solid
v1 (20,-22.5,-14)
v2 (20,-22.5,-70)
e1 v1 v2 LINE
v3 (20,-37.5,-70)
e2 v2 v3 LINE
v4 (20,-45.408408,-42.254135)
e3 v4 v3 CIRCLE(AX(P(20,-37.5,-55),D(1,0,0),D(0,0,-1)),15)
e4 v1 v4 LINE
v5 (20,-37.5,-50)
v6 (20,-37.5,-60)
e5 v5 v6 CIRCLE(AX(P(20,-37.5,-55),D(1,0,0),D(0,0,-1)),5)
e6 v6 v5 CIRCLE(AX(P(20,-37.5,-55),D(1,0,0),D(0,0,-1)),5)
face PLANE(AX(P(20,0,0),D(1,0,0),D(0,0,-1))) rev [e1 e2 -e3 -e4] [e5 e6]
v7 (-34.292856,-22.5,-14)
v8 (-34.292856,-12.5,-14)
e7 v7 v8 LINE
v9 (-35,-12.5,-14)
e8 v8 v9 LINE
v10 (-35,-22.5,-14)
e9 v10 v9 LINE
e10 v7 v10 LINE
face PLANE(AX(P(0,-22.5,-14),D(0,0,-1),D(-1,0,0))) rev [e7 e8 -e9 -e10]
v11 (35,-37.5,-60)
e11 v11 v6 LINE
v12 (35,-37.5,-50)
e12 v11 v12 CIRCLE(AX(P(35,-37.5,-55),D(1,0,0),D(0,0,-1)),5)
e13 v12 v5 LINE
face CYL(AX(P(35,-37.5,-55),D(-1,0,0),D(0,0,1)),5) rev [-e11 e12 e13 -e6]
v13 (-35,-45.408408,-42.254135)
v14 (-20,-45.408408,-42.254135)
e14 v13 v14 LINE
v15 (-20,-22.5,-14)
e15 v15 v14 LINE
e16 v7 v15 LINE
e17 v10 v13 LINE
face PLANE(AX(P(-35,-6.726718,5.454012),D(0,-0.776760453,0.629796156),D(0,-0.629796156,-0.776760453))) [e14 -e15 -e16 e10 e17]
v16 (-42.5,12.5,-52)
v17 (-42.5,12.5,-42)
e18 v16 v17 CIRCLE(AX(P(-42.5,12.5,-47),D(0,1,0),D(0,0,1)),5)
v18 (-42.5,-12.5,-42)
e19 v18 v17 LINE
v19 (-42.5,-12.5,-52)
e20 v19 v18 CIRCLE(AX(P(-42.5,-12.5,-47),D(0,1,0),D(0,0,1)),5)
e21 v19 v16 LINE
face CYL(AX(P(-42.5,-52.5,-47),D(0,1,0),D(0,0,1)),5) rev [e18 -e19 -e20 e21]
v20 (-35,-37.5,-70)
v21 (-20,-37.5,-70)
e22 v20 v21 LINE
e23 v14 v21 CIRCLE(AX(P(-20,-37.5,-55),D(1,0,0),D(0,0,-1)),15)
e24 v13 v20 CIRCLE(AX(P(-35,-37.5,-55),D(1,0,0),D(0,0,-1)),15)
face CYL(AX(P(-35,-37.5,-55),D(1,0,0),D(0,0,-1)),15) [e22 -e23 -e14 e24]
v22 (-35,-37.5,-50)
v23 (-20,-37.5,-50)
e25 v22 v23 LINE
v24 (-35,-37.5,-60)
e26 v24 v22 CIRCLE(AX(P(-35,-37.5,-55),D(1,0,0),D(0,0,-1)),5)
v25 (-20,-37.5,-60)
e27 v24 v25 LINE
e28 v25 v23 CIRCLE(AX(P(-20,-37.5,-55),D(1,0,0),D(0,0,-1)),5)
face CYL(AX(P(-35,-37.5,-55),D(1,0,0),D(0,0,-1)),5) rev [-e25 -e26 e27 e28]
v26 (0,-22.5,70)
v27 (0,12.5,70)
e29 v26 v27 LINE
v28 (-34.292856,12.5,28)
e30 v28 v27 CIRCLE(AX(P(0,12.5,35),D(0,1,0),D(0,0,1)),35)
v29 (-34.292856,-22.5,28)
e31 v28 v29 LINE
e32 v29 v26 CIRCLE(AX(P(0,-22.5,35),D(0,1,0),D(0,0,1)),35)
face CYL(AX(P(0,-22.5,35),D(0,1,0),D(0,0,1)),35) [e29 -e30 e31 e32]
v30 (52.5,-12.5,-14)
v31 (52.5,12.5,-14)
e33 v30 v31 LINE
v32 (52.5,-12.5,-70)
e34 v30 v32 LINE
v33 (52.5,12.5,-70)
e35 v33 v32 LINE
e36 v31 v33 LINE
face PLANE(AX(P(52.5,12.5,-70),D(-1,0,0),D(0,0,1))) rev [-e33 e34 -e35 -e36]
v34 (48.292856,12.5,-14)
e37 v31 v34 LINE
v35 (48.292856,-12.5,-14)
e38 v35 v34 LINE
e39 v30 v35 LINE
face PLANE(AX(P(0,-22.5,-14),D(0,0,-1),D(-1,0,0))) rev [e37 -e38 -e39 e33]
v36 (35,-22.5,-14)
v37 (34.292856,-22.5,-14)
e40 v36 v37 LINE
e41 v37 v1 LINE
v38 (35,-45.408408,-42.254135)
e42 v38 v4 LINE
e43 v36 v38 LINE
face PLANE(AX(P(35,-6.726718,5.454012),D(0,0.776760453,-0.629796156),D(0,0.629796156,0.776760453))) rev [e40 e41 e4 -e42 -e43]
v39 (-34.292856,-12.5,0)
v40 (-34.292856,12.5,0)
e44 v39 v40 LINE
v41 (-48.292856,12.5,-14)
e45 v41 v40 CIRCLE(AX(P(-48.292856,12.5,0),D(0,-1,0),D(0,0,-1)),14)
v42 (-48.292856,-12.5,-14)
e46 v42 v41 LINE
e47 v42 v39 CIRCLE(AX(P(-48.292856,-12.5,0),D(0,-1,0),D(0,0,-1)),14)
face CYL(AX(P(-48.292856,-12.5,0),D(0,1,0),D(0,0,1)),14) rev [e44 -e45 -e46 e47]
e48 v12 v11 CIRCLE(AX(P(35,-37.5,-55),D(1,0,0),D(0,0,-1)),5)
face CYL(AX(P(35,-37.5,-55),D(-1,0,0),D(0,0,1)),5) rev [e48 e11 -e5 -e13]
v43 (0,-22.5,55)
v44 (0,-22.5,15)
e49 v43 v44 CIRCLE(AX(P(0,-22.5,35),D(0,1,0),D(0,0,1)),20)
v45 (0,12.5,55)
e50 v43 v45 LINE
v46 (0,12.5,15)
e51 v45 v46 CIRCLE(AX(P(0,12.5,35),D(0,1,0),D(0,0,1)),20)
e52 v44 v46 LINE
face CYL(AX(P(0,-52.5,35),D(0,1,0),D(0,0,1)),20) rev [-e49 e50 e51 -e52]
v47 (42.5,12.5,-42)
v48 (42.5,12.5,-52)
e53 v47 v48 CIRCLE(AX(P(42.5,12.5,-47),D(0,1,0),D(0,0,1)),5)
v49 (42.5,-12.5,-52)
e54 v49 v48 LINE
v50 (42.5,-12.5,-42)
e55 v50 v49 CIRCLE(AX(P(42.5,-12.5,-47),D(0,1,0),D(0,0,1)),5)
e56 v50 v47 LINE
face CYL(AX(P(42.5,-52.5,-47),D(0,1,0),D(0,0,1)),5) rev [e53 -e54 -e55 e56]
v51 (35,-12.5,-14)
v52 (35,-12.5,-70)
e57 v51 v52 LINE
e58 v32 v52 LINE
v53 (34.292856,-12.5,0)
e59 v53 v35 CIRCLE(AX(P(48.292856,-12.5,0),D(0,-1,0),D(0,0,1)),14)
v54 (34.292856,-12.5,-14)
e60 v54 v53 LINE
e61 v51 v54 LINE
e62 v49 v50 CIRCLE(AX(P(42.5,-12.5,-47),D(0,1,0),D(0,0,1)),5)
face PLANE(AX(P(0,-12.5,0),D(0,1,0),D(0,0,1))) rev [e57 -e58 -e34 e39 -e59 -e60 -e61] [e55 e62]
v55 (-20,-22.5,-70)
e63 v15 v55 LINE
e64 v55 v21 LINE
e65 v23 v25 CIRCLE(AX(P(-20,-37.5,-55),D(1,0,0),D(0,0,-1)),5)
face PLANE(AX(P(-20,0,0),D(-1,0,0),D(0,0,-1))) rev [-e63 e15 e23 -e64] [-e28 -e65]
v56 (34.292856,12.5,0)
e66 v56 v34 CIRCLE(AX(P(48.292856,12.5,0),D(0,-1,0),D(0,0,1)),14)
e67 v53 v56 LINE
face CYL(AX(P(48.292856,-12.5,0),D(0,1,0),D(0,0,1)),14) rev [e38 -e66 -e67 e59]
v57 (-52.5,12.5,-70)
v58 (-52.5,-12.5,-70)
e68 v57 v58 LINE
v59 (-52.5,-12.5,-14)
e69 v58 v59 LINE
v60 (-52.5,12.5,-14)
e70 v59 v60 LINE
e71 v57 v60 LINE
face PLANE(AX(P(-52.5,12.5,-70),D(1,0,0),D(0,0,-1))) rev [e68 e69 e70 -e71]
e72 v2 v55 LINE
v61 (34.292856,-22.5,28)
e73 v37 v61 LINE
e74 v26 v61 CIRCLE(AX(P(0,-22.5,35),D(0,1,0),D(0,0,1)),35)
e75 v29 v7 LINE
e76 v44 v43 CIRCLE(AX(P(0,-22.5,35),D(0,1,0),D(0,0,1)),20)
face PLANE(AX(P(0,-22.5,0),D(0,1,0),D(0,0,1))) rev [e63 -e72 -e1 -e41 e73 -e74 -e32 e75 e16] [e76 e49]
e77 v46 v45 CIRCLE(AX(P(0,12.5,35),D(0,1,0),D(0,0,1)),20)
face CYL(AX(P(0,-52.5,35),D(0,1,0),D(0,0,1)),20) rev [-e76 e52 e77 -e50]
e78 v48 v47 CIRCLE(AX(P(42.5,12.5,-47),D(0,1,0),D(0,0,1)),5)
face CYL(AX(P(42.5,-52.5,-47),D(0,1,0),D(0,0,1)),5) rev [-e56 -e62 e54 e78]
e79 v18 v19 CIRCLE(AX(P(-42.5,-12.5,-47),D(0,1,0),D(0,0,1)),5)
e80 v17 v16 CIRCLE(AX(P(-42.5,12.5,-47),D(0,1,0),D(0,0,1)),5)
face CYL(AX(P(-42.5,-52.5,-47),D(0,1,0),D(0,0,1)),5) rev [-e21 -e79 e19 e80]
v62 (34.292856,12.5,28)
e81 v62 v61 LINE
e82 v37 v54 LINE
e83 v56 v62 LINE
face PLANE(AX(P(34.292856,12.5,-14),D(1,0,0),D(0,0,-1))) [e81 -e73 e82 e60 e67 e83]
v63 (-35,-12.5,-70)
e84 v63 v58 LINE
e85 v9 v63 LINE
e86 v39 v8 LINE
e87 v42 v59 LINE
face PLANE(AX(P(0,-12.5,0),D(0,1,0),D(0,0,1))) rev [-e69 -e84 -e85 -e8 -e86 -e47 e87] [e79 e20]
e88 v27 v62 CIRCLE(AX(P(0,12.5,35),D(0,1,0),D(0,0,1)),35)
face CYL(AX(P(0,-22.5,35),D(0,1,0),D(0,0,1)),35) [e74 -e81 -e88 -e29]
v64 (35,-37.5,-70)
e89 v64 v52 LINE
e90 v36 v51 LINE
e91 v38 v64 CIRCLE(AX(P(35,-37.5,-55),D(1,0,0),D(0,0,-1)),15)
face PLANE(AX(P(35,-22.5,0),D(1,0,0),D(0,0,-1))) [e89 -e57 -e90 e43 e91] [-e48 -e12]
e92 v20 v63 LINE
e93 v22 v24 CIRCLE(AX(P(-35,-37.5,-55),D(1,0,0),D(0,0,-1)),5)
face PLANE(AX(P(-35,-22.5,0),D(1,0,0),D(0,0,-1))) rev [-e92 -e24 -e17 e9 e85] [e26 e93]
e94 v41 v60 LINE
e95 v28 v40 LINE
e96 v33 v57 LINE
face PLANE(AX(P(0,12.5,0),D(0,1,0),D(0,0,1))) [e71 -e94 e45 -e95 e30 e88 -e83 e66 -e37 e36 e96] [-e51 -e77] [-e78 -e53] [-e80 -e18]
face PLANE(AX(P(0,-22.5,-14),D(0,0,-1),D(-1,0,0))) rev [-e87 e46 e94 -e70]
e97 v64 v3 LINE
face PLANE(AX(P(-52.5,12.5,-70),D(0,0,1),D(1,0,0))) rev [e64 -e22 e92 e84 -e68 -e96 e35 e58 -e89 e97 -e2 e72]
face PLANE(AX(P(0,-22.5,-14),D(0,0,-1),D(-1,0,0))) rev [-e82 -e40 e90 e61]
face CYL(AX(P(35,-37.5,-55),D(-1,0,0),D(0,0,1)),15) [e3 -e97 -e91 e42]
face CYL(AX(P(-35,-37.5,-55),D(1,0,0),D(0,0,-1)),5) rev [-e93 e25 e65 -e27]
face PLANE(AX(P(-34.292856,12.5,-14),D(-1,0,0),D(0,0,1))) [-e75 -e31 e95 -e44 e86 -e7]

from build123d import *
from build123d.topology import SkipClean

# Parameters (mm, degrees)
BASE_PLATE_SKETCH_140X105_W  = 105
BASE_PLATE_SKETCH_140X105_H  = 140
BASE_PLATE_DEPTH             = 12.5
HUB_BOSS_DEPTH               = 35
BORE_RELIEF_56_DEPTH         = 95.240384125
FILLER_START                 = -35
FILLER_BOSS_DEPTH            = 35
LUG_BOSS_DEPTH               = 25
SIDE_START                   = 20
SIDE_EAR_SKETCH_R            = 5
SIDE_EAR_DEPTH               = 15
MOUNTING_HOLES_SKETCH_10_R   = 5
MOUNTING_HOLES_SKETCH_10_R_2 = 20
MOUNTING_HOLES_10_DEPTH      = 110.001146783


with BuildPart() as part:
    # Base Plate Sketch 140x105 → Base Plate (new, symmetric)
    with BuildSketch(Plane(origin=(0, 0, 0), x_dir=(1, 0, 0), z_dir=(0, 1, 0))):
        Rectangle(BASE_PLATE_SKETCH_140X105_W, BASE_PLATE_SKETCH_140X105_H)
    extrude(amount=BASE_PLATE_DEPTH, both=True)

    # Hub Boss Sketch → Hub Boss (add)
    with BuildSketch(Plane(origin=(0, 12.5, 0), x_dir=(1, 0, 0), z_dir=(0, 1, 0))):
        with BuildLine():
            Line((-17.5, 70), (-35, 70))
            Line((-35, 70), (-35, 14))
            Line((-35, 14), (-35, -35))
            ThreePointArc((-35, -35), (-24.748737337, -59.748737346), (1.3e-08, -70))
            ThreePointArc((1.3e-08, -70), (24.748737346, -59.748737337), (35, -35))
            Line((35, -35), (35, 14))
            Line((35, 14), (35, 70))
            Line((35, 70), (17.5, 70))
            Line((17.5, 70), (-17.5, 70))
        make_face()
    extrude(amount=-HUB_BOSS_DEPTH)

    # Bore Relief Sketch _56 → Bore Relief _56 (cut, through all)
    with SkipClean():  # the faces are left unmerged after this step: merging them gives an invalid solid
        with BuildSketch(Plane(origin=(0, 12.5, 0), x_dir=(1, 0, 0), z_dir=(0, 1, 0))):
            with BuildLine():
                Line((-52.5, -70), (6e-09, -70))
                ThreePointArc((6e-09, -70), (-24.748737339, -59.748737344), (-35, -35))
                ThreePointArc((-35, -35), (-32.267021942, -21.441264992), (-24.494897428, -10))
                ThreePointArc((-24.494897428, -10), (-21.331375002, 5.291502622), (-34.292856399, 14))
                Line((-34.292856399, 14), (-52.5, 14))
                Line((-52.5, 14), (-52.5, -70))
            make_face()
            with BuildLine():
                Line((52.5, -70), (52.5, 14))
                Line((52.5, 14), (34.292856399, 14))
                ThreePointArc((34.292856399, 14), (21.331375002, 5.291502622), (24.494897428, -10))
                ThreePointArc((24.494897428, -10), (32.267021942, -21.441264992), (35, -35))
                ThreePointArc((35, -35), (24.748737344, -59.748737339), (6e-09, -70))
                Line((6e-09, -70), (52.5, -70))
            make_face()
        extrude(amount=-BORE_RELIEF_56_DEPTH, mode=Mode.SUBTRACT)

    # Filler Boss Sketch → Filler Boss (add)
    with SkipClean():  # the faces are left unmerged after this step: merging them gives an invalid solid
        with BuildSketch(Plane.XZ.offset(22.5).offset(FILLER_START)):
            with BuildLine():
                Line((-34.292856399, -14), (-34.292856399, 28))
                ThreePointArc((-34.292856399, 28), (-30.740852298, 18.266799469), (-24.494897428, 10))
                ThreePointArc((-24.494897428, 10), (-21.331375002, -5.291502622), (-34.292856399, -14))
            make_face()
            with BuildLine():
                Line((34.292856399, -14), (34.292856399, 28))
                ThreePointArc((34.292856399, 28), (30.740852298, 18.266799469), (24.494897428, 10))
                ThreePointArc((24.494897428, 10), (21.331375002, -5.291502622), (34.292856399, -14))
            make_face()
        extrude(amount=FILLER_BOSS_DEPTH)

    # Lug Boss Sketch → Lug Boss (add)
    with SkipClean():  # the faces are left unmerged after this step: merging them gives an invalid solid
        with BuildSketch(Plane(origin=(0, 12.5, 0), x_dir=(1, 0, 0), z_dir=(0, 1, 0))):
            with BuildLine():
                Line((48.292856399, 14), (34.292856399, 14))
                Line((34.292856399, 14), (34.292856399, 0))
                ThreePointArc((34.292856399, 0), (38.393361462, 9.899494937), (48.292856399, 14))
            make_face()
            with BuildLine():
                Line((-34.292856399, 0), (-34.292856399, 14))
                Line((-34.292856399, 14), (-48.292856399, 14))
                ThreePointArc((-48.292856399, 14), (-38.393361462, 9.899494937), (-34.292856399, 0))
            make_face()
        extrude(amount=-LUG_BOSS_DEPTH)

    # Side Ear Sketch → Side Ear (add)
    with SkipClean():  # the faces are left unmerged after this step: merging them gives an invalid solid
        with BuildSketch(Plane(origin=(0, 0, 0), x_dir=(0, 0, -1), z_dir=(1, 0, 0)).offset(SIDE_START)):
            with BuildLine():
                Line((70, -37.5), (70, -22.5))
                Line((70, -22.5), (14, -22.5))
                Line((14, -22.5), (42.254134702, -45.408408045))
                ThreePointArc((42.254134702, -45.408408045), (47.707062344, -50.607748103), (55, -52.5))
                ThreePointArc((55, -52.5), (65.606601718, -48.106601718), (70, -37.5))
            make_face()
            with Locations((55, -37.5)):
                Circle(SIDE_EAR_SKETCH_R, mode=Mode.SUBTRACT)
        side_ear = extrude(amount=SIDE_EAR_DEPTH)

    # Side Ear Mirror: Side Ear across plane
    with SkipClean():  # the faces are left unmerged after this step: merging them gives an invalid solid
        add(side_ear.mirror(Plane(origin=(0, 0, 0), x_dir=(0, 0, 1), z_dir=(1, 0, 0))))

    # Mounting Holes Sketch _10 → Mounting Holes _10 (cut, through all)
    with SkipClean():  # the faces are left unmerged after this step: merging them gives an invalid solid
        with BuildSketch(Plane(origin=(0, 12.5, 0), x_dir=(1, 0, 0), z_dir=(0, 1, 0))):
            with Locations(Location((-42.5, 47, 0), (0, 0, 270))):
                Circle(MOUNTING_HOLES_SKETCH_10_R)
            with Locations(Location((42.5, 47, 0), (0, 0, 270))):
                Circle(MOUNTING_HOLES_SKETCH_10_R)
            with Locations(Location((0, -35, 0), (0, 0, 270))):
                Circle(MOUNTING_HOLES_SKETCH_10_R_2)
        extrude(amount=-MOUNTING_HOLES_10_DEPTH, mode=Mode.SUBTRACT)


solid = part.part
